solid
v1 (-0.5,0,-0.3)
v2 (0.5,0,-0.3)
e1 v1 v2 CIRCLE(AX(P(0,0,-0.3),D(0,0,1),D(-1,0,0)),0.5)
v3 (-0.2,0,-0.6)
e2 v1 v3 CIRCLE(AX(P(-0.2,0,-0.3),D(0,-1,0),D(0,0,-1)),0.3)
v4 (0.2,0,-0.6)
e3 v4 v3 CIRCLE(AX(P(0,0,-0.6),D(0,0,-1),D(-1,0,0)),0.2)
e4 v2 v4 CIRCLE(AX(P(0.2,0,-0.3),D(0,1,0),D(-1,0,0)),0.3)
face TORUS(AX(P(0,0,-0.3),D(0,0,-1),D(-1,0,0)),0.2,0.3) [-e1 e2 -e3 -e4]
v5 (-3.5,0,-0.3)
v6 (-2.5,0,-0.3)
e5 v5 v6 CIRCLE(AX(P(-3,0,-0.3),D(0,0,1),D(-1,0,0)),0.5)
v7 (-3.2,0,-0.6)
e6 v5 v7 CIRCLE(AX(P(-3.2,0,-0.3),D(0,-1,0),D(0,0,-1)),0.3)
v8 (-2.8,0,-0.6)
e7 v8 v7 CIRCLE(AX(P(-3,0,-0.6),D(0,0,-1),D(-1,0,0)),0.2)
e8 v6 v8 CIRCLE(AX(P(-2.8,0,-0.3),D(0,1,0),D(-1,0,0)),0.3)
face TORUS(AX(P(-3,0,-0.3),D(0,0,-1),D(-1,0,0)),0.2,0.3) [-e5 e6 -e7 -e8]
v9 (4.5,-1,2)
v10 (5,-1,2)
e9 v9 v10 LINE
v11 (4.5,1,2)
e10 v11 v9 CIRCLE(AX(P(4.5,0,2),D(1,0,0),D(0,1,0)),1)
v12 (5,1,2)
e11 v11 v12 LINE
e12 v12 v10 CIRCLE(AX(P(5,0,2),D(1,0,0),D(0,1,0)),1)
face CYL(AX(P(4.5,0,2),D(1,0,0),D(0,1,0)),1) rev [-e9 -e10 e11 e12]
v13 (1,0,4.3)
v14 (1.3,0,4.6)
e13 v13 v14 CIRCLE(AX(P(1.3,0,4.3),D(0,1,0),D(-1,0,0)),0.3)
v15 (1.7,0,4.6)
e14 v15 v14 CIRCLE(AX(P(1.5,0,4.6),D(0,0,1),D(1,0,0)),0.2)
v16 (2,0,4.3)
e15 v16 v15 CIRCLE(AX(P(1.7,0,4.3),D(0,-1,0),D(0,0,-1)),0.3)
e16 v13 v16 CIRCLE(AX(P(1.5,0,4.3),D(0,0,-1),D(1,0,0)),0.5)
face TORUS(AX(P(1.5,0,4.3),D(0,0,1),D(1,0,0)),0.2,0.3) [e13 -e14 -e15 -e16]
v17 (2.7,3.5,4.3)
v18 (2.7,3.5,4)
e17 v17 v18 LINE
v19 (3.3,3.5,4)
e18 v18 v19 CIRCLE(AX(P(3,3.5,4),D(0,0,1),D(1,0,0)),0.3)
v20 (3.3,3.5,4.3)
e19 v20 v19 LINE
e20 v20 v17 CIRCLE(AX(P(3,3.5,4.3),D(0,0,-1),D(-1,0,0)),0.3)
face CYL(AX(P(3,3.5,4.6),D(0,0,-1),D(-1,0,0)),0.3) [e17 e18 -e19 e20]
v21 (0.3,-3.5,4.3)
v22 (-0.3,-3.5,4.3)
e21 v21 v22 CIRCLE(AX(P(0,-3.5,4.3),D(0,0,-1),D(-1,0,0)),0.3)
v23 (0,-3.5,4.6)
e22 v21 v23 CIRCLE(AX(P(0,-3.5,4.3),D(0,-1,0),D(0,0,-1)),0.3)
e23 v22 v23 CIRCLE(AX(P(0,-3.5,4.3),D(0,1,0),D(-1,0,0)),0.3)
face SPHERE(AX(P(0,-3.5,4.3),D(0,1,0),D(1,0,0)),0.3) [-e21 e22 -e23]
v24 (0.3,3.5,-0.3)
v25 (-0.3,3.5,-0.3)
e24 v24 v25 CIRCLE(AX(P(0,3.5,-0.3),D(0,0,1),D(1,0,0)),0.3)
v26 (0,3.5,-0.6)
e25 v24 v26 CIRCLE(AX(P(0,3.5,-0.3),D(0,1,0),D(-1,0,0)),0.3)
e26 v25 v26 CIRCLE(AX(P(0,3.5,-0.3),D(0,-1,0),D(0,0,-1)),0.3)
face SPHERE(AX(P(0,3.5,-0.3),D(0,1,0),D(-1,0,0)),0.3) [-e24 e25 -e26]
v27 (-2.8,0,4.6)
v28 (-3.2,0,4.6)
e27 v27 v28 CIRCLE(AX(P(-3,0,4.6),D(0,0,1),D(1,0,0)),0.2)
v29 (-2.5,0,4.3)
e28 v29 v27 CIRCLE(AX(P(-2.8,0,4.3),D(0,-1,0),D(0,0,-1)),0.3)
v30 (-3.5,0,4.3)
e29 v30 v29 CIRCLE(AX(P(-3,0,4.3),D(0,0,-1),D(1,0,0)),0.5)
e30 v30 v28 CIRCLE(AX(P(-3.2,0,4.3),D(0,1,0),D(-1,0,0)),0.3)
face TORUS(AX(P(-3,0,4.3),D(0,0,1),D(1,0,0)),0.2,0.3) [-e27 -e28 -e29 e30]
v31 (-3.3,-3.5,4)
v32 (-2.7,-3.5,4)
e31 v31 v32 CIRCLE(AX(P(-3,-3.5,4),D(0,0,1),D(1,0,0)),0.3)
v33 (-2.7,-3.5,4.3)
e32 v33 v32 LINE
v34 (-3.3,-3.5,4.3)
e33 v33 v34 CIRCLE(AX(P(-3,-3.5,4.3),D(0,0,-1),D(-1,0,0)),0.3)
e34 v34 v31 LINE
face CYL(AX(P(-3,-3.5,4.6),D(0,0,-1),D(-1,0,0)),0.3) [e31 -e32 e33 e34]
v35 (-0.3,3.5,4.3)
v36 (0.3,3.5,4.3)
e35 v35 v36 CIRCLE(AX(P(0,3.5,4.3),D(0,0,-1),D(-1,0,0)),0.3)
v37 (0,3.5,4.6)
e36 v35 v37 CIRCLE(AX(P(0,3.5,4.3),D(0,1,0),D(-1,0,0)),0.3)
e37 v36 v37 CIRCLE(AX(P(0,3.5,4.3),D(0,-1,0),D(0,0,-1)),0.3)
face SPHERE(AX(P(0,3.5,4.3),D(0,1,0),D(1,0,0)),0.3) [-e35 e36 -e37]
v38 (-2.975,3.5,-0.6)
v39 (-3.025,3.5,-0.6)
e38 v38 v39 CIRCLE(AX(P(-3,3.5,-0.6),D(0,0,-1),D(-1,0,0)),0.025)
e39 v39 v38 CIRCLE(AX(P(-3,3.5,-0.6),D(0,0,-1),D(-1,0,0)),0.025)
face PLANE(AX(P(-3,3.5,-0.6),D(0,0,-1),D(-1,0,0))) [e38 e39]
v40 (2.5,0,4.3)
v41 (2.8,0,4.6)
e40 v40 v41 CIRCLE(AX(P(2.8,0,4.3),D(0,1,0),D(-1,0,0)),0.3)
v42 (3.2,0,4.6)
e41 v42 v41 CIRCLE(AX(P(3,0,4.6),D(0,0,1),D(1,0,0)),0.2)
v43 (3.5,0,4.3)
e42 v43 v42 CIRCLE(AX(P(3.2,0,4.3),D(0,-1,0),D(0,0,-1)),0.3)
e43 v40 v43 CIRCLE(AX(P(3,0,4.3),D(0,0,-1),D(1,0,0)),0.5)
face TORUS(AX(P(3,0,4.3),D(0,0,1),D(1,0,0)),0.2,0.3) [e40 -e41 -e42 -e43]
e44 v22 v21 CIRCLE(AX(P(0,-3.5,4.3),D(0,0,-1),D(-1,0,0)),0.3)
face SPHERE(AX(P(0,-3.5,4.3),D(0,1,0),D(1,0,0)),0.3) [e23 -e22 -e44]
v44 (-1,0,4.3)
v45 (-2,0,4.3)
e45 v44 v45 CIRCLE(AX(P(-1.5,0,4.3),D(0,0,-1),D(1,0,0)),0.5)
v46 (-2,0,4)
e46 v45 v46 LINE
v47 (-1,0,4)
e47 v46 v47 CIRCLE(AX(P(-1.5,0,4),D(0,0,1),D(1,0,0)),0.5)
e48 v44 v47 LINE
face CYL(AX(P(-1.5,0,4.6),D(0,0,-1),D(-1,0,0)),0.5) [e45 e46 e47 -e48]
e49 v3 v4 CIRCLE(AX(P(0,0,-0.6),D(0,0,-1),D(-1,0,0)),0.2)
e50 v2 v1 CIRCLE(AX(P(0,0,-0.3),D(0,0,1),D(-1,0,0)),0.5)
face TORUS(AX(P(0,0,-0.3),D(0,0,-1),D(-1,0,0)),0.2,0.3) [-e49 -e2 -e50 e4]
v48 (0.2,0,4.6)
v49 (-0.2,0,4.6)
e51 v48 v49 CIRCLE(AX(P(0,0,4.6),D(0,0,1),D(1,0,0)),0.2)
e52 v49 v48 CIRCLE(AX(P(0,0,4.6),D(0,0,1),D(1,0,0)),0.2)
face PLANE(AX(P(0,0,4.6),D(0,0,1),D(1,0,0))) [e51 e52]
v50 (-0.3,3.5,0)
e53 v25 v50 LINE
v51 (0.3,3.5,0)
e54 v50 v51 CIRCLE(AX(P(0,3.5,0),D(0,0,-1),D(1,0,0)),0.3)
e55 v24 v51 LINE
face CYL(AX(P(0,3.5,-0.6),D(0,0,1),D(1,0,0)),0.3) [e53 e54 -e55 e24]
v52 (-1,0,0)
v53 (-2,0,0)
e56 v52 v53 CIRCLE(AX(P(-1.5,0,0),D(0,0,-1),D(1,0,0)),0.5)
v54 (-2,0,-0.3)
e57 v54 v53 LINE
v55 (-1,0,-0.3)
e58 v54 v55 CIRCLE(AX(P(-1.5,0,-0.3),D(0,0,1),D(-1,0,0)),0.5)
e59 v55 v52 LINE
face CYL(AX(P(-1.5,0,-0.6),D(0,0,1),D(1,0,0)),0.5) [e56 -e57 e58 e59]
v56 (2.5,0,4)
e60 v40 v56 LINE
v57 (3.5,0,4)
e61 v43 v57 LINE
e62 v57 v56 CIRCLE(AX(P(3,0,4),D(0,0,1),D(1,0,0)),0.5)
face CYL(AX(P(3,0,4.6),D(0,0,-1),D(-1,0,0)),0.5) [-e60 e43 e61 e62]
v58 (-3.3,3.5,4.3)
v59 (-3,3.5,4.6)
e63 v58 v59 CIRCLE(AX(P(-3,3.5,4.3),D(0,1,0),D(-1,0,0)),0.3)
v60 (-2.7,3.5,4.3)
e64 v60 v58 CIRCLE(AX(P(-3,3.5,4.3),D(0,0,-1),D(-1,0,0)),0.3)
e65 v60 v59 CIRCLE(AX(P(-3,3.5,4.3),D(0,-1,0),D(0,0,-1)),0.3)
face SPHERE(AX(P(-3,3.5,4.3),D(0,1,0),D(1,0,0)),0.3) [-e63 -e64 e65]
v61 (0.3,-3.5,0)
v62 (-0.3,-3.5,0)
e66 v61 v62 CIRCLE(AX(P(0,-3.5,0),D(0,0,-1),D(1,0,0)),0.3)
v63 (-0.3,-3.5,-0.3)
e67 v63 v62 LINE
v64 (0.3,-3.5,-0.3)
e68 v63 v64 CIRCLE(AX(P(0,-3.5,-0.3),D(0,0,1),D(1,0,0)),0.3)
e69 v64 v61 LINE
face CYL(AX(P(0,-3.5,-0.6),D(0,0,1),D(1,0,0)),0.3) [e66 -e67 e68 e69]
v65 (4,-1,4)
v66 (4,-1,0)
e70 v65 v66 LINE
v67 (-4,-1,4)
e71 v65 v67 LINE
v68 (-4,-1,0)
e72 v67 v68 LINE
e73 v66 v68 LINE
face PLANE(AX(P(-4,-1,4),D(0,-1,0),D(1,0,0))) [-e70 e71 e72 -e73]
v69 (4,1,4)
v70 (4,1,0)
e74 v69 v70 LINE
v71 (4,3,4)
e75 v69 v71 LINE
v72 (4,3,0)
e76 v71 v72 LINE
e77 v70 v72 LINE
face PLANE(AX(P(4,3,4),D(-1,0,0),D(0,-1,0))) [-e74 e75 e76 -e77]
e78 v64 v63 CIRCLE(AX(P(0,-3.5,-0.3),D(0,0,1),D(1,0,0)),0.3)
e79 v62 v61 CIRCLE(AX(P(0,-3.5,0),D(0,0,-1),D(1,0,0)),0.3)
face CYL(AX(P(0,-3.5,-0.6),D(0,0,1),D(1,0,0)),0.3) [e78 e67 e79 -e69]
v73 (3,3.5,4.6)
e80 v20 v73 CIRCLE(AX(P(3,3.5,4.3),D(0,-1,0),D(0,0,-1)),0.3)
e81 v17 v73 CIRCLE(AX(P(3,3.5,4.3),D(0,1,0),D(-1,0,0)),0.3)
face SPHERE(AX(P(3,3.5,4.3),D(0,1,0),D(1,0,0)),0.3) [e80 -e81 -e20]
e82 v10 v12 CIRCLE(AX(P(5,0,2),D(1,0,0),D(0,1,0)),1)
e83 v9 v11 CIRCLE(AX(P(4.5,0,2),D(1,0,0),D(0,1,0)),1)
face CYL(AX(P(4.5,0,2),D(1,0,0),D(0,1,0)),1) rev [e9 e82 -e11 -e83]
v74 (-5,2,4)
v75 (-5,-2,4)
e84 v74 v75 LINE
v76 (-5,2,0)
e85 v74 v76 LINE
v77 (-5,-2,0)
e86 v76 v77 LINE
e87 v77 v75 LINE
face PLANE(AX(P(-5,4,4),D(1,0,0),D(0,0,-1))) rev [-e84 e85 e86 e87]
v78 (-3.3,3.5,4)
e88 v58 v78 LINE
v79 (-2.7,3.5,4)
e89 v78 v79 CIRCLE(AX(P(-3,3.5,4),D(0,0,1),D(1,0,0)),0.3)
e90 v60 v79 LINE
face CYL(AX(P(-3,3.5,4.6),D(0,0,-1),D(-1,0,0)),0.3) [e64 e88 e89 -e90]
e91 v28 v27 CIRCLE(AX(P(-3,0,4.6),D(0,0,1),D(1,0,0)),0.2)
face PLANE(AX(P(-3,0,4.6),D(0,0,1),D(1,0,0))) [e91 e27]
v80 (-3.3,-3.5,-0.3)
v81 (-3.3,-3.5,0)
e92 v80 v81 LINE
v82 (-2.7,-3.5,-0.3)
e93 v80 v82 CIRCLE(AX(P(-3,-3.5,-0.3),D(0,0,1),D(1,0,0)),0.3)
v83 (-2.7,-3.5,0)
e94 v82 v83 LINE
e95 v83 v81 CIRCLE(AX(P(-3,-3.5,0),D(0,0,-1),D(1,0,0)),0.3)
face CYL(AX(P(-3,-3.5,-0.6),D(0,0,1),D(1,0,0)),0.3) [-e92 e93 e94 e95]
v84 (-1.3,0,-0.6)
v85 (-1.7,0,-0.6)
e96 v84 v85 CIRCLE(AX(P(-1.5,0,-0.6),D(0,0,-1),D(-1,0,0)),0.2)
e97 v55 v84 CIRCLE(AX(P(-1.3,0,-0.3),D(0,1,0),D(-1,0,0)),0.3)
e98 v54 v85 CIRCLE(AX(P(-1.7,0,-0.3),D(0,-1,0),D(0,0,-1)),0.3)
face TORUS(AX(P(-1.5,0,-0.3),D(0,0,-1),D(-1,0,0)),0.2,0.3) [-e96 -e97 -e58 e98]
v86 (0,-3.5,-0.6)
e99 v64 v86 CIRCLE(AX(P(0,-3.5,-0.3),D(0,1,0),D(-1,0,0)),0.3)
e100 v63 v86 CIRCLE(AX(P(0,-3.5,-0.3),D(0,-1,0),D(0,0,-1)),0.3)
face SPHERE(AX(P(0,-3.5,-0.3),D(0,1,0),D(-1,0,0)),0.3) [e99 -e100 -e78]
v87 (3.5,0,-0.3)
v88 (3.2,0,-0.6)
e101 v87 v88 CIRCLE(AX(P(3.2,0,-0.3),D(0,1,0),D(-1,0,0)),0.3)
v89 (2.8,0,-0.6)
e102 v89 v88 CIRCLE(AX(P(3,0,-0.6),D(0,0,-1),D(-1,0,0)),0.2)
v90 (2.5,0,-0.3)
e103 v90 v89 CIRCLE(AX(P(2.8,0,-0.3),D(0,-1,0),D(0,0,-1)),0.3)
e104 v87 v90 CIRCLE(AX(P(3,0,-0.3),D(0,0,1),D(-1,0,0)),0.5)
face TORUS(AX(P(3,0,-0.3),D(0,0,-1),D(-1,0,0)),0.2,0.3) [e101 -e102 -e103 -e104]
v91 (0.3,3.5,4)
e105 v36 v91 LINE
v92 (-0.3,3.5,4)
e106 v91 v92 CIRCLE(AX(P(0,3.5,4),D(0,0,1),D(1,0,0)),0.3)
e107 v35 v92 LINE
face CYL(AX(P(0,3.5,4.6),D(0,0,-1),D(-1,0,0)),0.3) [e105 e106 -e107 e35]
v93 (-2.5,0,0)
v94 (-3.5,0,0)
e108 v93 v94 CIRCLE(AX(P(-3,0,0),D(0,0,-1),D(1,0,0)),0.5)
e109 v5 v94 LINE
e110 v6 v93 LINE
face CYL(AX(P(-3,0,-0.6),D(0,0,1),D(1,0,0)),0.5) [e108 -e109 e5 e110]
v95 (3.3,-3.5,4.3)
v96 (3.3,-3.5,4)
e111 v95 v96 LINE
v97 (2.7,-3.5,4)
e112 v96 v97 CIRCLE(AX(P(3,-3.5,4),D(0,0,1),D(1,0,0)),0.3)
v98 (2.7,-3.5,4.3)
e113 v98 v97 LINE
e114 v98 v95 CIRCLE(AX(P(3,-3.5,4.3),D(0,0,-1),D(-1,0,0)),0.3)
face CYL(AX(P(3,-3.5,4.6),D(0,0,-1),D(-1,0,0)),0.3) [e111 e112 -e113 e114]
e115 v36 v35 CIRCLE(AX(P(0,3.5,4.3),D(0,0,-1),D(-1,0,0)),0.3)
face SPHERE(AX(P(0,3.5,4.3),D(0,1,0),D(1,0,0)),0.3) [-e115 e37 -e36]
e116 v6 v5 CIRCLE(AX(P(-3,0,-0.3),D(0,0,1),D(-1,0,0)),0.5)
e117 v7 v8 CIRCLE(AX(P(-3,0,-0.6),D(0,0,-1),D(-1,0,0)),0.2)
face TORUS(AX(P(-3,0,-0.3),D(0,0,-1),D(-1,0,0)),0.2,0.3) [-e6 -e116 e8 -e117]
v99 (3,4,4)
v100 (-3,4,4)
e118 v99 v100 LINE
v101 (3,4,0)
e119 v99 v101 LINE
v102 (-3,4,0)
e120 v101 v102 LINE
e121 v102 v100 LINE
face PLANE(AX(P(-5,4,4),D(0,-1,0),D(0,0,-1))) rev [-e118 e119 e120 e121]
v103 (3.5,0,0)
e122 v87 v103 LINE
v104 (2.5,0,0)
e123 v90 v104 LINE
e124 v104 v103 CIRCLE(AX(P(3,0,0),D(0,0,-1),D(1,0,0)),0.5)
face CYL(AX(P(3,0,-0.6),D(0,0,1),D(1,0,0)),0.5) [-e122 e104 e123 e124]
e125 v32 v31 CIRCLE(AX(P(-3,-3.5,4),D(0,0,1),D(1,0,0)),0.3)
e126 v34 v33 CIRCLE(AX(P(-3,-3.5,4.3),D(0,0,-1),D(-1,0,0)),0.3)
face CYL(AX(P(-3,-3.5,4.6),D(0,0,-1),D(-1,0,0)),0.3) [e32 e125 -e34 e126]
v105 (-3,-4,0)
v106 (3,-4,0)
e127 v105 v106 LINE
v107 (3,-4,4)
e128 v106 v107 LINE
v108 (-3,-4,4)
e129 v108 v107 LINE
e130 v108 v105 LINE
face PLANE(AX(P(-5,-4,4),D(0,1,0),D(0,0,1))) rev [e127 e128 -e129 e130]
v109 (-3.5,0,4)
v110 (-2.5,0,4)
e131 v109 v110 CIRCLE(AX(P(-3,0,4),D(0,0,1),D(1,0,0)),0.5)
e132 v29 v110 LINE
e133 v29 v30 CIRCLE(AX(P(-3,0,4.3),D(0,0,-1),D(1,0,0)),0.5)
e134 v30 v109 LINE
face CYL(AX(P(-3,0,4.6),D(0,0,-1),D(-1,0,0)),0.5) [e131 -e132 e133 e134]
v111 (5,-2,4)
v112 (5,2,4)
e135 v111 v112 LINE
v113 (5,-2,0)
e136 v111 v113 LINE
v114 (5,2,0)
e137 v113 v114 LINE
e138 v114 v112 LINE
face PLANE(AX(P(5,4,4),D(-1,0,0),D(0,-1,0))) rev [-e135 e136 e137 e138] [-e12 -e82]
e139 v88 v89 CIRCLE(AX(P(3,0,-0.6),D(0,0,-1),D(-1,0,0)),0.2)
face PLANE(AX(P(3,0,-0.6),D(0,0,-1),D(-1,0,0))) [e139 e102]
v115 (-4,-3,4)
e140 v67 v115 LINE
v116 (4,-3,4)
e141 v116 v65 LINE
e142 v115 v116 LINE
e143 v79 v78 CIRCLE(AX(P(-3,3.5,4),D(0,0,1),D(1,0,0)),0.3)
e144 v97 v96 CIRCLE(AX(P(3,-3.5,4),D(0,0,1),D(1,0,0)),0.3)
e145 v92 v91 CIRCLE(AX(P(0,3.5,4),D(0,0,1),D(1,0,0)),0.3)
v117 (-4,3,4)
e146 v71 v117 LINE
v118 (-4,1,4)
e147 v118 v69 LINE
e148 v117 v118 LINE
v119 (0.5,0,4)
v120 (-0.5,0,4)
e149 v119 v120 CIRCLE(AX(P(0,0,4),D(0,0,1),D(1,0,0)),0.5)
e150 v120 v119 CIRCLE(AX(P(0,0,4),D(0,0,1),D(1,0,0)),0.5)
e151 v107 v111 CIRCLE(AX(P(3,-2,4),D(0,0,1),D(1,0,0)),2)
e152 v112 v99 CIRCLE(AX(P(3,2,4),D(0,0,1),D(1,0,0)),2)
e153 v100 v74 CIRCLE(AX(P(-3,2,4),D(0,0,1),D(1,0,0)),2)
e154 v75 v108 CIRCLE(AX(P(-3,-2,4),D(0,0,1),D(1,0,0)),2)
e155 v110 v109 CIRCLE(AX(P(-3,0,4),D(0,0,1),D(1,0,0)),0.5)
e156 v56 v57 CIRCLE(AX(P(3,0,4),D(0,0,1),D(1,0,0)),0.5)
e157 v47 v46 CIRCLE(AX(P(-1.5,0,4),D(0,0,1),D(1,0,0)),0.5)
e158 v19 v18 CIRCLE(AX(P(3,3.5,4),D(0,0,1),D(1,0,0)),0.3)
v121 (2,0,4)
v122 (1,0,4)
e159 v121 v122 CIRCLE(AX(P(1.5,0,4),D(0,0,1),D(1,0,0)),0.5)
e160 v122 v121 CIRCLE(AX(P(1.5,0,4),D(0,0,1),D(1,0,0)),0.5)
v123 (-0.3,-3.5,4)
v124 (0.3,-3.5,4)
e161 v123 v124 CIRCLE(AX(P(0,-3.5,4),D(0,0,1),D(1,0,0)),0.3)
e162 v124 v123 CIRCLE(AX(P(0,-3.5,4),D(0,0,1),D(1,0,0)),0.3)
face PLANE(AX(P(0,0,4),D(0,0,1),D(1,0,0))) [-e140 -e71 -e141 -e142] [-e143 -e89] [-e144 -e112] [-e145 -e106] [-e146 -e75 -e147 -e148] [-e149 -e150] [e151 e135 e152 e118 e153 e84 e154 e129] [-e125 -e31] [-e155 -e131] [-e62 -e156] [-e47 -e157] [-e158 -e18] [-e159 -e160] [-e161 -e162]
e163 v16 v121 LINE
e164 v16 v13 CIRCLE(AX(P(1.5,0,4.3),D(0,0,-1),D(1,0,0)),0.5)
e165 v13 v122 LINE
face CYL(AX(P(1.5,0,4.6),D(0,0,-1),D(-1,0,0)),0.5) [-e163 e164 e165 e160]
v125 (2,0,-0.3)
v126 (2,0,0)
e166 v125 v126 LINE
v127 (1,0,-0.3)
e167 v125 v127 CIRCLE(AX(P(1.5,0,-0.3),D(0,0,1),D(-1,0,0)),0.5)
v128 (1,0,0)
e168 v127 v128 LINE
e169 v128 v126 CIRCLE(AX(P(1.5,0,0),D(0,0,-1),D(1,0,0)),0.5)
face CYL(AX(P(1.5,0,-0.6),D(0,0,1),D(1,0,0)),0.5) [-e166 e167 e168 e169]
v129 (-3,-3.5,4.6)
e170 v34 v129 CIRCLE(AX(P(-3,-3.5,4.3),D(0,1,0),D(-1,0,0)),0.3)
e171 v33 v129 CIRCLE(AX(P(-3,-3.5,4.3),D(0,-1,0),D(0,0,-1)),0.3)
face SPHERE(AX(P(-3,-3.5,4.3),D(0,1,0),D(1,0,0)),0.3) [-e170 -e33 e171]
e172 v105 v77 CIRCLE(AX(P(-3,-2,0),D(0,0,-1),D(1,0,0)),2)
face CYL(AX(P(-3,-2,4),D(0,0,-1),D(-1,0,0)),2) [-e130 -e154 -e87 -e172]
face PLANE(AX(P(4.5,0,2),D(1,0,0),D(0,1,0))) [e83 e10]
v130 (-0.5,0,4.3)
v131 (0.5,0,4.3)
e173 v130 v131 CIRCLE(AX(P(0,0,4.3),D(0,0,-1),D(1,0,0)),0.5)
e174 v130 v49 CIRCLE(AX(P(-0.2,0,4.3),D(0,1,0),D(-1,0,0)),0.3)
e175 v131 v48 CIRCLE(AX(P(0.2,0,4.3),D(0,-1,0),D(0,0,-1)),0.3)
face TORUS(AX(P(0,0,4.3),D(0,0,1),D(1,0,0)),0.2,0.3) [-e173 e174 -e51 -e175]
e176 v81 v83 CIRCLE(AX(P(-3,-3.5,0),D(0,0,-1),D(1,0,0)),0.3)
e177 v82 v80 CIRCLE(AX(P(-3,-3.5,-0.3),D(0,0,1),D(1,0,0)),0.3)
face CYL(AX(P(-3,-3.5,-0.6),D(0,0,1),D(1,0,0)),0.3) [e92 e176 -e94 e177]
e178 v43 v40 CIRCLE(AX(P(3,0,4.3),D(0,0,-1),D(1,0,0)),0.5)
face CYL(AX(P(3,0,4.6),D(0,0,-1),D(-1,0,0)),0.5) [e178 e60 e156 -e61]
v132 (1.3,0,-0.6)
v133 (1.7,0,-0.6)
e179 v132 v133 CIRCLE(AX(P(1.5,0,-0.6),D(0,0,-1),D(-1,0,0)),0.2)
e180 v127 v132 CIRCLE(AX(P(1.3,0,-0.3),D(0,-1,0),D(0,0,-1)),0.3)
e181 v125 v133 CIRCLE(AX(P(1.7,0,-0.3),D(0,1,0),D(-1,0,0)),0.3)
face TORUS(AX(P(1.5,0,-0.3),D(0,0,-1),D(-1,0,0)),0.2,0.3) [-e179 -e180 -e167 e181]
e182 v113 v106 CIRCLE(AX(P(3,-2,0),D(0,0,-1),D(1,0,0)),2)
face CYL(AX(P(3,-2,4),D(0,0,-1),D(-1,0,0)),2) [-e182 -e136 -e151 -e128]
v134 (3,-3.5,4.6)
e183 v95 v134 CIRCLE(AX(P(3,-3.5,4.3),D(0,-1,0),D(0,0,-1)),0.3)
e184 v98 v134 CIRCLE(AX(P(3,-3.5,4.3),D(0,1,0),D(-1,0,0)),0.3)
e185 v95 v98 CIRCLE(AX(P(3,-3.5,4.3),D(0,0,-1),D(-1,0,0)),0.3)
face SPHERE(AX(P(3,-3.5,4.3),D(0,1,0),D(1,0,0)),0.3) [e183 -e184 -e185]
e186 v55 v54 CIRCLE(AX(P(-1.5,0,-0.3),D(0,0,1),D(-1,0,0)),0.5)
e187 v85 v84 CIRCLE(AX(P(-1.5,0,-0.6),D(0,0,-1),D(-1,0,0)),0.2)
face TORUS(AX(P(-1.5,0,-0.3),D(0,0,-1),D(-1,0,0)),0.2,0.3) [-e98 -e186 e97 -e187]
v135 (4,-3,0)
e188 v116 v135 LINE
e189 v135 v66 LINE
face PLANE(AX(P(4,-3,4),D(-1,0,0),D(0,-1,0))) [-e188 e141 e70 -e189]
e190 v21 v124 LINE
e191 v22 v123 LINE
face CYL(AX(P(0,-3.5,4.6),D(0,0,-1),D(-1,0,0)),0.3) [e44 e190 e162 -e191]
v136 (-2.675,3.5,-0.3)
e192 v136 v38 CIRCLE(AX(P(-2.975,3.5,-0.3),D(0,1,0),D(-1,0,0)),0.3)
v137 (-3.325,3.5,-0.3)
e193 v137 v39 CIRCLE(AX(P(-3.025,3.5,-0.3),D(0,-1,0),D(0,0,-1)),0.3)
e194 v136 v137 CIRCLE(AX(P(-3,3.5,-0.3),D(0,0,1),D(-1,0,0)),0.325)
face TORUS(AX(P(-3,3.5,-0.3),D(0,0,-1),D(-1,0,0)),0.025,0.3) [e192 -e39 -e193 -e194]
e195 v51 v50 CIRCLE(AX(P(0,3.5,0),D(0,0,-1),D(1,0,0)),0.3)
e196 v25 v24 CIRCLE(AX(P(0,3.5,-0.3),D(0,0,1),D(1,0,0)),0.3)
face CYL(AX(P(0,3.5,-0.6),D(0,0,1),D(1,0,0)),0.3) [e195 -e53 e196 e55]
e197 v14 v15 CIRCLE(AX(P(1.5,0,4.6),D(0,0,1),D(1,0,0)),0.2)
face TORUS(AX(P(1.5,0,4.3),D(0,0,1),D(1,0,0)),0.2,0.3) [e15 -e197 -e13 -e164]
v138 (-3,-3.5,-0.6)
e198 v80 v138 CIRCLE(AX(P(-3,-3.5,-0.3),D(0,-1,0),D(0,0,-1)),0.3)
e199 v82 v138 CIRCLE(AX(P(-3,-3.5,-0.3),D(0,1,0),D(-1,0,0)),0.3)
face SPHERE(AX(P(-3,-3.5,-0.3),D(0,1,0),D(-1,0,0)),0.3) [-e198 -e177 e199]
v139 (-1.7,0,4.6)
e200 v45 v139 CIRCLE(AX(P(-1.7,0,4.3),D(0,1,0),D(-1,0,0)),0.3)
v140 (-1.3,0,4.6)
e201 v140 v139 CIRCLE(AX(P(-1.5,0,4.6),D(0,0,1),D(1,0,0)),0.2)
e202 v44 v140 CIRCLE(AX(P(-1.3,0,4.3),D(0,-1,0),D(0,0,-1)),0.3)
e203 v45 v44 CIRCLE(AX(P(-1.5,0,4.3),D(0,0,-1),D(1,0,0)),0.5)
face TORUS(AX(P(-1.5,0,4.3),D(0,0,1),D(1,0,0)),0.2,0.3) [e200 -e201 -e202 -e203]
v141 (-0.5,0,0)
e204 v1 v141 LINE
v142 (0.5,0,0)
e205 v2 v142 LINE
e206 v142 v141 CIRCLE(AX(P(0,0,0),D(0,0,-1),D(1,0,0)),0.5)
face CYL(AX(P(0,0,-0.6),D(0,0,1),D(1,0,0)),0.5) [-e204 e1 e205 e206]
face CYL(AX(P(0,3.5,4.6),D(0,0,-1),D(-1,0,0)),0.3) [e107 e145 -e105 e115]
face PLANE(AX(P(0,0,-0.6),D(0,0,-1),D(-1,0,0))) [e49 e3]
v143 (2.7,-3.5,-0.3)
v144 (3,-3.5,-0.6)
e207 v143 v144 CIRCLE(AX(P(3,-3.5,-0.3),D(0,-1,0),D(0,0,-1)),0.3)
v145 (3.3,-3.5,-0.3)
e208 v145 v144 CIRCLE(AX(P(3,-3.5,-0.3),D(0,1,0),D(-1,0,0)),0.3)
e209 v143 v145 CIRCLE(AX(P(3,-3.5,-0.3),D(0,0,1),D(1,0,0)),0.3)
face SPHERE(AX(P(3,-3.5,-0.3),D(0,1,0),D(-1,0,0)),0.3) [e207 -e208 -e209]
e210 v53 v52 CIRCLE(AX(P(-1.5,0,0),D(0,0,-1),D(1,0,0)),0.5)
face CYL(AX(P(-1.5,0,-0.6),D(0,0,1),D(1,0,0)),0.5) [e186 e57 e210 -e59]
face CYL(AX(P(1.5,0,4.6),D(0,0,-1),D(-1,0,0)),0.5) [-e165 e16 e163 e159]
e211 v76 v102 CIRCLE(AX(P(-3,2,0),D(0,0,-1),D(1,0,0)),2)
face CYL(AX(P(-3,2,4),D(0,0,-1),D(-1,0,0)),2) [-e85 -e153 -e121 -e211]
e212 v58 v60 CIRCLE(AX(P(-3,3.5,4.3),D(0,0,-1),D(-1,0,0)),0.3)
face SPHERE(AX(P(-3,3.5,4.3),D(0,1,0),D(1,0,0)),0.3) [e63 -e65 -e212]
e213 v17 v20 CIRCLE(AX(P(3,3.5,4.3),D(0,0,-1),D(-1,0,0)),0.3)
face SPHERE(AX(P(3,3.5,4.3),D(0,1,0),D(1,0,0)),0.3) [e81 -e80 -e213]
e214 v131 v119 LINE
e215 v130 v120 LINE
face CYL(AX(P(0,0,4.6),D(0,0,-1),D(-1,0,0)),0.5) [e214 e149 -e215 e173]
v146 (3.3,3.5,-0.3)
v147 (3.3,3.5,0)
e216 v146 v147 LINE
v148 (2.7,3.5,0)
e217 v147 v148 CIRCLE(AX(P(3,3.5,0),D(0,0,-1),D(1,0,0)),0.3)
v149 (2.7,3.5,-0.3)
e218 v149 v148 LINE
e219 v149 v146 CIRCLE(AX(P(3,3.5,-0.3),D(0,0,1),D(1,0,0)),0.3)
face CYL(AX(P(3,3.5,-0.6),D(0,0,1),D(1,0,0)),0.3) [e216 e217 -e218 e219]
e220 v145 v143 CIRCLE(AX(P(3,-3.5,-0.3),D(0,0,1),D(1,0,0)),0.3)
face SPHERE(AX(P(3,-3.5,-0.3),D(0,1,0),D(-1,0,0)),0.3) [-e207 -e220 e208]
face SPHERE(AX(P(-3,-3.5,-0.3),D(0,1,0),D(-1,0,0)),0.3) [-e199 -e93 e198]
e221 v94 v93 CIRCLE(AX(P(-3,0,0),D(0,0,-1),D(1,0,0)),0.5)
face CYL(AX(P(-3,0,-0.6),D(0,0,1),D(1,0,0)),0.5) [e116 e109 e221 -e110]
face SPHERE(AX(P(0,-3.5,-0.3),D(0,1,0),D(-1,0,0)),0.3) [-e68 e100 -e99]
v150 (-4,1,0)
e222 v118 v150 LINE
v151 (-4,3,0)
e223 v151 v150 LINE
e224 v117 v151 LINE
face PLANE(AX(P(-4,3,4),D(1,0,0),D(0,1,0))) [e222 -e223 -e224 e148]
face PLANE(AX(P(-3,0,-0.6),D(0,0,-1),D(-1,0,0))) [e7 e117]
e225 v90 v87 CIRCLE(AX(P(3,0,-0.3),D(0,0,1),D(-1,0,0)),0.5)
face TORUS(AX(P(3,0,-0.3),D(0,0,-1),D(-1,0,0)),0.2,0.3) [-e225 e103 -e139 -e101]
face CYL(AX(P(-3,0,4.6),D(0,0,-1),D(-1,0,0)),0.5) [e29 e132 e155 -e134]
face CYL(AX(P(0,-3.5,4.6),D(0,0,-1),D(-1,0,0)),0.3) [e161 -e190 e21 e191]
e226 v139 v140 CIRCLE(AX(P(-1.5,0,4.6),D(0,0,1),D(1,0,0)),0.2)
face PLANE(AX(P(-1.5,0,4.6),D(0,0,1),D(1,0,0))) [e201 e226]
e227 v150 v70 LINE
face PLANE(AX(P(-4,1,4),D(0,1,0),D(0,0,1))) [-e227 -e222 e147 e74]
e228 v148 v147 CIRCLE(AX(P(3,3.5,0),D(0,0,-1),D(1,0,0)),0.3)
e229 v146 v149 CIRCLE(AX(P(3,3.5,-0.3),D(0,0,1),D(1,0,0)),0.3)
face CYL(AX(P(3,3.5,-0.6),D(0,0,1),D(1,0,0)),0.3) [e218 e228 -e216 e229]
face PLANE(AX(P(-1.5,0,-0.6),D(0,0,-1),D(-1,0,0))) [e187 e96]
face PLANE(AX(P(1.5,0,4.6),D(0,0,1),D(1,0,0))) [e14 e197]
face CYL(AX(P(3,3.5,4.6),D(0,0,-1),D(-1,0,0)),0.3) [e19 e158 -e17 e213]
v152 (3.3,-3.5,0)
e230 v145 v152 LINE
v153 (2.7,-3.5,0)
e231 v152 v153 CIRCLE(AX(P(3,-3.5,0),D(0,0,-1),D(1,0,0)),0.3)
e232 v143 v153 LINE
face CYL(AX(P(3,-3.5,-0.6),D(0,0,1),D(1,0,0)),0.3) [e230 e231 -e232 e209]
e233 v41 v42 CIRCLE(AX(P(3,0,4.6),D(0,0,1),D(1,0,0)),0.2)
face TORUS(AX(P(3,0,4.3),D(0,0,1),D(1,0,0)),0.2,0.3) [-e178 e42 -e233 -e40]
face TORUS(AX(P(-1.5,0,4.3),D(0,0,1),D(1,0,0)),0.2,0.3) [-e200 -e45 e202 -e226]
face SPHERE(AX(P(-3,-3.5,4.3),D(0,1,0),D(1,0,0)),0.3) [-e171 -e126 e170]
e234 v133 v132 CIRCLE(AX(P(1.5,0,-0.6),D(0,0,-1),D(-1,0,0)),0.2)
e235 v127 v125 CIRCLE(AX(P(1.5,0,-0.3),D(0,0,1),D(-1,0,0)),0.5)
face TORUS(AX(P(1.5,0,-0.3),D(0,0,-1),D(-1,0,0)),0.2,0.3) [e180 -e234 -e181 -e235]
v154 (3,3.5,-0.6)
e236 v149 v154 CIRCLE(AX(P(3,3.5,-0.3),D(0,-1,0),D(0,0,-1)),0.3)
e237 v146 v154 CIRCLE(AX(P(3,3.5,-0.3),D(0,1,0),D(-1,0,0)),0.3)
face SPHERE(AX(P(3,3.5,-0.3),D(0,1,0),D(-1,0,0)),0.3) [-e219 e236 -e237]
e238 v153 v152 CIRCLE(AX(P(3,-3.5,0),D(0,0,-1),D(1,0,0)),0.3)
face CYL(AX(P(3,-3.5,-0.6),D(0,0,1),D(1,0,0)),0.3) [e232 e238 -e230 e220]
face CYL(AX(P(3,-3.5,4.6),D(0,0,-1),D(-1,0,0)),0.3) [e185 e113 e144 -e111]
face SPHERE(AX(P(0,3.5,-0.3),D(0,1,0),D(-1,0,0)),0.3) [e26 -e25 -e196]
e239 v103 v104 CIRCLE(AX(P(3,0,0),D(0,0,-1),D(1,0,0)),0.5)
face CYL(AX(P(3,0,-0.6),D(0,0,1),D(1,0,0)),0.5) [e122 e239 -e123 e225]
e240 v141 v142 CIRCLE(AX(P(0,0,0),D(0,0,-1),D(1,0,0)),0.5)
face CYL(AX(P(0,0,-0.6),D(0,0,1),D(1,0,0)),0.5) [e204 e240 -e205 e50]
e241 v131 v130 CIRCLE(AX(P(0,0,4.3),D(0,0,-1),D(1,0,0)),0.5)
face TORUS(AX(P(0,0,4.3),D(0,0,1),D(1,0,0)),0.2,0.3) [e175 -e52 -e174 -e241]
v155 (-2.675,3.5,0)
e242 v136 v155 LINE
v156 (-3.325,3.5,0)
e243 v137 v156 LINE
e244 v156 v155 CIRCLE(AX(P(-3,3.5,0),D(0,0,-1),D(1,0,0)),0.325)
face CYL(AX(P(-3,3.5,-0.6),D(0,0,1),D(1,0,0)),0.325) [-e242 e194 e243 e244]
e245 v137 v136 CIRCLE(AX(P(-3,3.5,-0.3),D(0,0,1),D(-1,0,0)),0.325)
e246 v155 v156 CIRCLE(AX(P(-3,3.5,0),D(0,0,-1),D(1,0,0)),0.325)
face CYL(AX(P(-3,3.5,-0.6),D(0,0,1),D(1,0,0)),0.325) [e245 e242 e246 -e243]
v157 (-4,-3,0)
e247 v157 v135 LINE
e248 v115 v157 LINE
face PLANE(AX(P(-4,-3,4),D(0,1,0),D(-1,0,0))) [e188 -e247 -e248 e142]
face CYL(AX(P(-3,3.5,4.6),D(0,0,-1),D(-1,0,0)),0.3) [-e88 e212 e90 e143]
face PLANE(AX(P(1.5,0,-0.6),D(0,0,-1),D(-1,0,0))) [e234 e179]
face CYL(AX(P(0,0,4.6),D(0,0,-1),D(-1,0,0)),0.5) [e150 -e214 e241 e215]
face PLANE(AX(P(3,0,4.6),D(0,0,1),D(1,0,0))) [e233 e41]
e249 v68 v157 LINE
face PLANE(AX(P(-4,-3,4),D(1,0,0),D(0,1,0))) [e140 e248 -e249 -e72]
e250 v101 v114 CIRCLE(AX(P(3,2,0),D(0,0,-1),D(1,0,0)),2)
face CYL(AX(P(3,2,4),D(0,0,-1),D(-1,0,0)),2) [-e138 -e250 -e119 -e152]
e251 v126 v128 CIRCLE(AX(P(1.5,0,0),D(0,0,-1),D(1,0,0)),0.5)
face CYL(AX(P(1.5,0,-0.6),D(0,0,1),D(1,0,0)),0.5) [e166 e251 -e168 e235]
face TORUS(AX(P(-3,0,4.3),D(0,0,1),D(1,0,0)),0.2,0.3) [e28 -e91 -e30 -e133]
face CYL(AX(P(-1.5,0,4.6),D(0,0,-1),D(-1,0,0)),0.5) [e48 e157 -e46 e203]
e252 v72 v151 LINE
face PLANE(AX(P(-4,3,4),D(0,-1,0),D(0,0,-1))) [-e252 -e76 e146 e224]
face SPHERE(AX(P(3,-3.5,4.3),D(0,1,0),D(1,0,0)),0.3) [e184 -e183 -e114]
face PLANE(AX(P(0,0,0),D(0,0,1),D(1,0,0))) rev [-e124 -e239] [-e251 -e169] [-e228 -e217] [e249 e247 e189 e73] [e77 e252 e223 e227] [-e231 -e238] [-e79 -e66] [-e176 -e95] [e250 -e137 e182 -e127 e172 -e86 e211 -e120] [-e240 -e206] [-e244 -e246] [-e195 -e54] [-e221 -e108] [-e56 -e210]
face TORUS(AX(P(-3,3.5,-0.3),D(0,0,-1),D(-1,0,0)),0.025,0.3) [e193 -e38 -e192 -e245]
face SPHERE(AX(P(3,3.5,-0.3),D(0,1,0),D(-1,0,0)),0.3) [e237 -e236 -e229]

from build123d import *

# Parameters (mm, degrees)
SKETCH1_W           = 10
SKETCH1_H           = 8
SKETCH1_W_2         = 8
SKETCH1_H_2         = 2
BOSS_EXTRUDE3_DEPTH = 4
SKETCH2_R           = 1
CUT_EXTRUDE6_DEPTH  = 0.5
FILLET1_R           = 2
SKETCH4_R           = 0.5
SKETCH4_R_2         = 0.3
BOSS_EXTRUDE7_DEPTH = 0.6
FILLET4_R           = 0.3
BOSS_EXTRUDE8_START = 0.6
SKETCH5_R           = 0.5
SKETCH5_R_2         = 0.3
SKETCH5_R_3         = 0.325
BOSS_EXTRUDE8_DEPTH = 0.6
FILLET5_R           = 0.3
FILLET6_R           = 0.3
FILLET7_R           = 0.3


with BuildPart() as part:
    # Sketch1 → Boss-Extrude3 (new body)
    with BuildSketch(Plane.XY):
        Rectangle(SKETCH1_W, SKETCH1_H)
        with Locations((0, 2)):
            Rectangle(SKETCH1_W_2, SKETCH1_H_2, mode=Mode.SUBTRACT)
        with Locations((0, -2)):
            Rectangle(SKETCH1_W_2, SKETCH1_H_2, mode=Mode.SUBTRACT)
    extrude(amount=BOSS_EXTRUDE3_DEPTH)

    # Sketch2 → Cut-Extrude6 (cut)
    with BuildSketch(Plane(origin=(5, 0, 0), x_dir=(0, 0, -1), z_dir=(1, 0, 0))):
        with Locations(Location((-2, 0, 0), (0, 0, 90))):
            Circle(SKETCH2_R)
    extrude(amount=-CUT_EXTRUDE6_DEPTH, mode=Mode.SUBTRACT)

    # Fillet1
    fillet1_edges = [part.edges().sort_by_distance(p)[0] for p in [
        (5, -4, 2),
        (-5, -4, 2),
        (-5, 4, 2),
        (5, 4, 2),
    ]]
    fillet(fillet1_edges, radius=FILLET1_R)

    # Sketch4 → Boss-Extrude7 (add)
    with BuildSketch(Plane.XY.offset(4)):
        Circle(SKETCH4_R)
        with Locations((-1.5, 0)):
            Circle(SKETCH4_R)
        with Locations((-3, 0)):
            Circle(SKETCH4_R)
        with Locations((1.5, 0)):
            Circle(SKETCH4_R)
        with Locations((3, 0)):
            Circle(SKETCH4_R)
        with Locations((3, -3.5)):
            Circle(SKETCH4_R_2)
        with Locations((0, -3.5)):
            Circle(SKETCH4_R_2)
        with Locations((-3, -3.5)):
            Circle(SKETCH4_R_2)
        with Locations((3, 3.5)):
            Circle(SKETCH4_R_2)
        with Locations((0, 3.5)):
            Circle(SKETCH4_R_2)
        with Locations((-3, 3.5)):
            Circle(SKETCH4_R_2)
    extrude(amount=BOSS_EXTRUDE7_DEPTH)

    # Fillet4
    fillet4_edges = [part.edges().sort_by_distance(p)[0] for p in [
        (-0.5, 0, 4.6),
        (-2, 0, 4.6),
        (-3.5, 0, 4.6),
        (1, 0, 4.6),
        (2.5, 0, 4.6),
    ]]
    fillet(fillet4_edges, radius=FILLET4_R)

    # Sketch5 → Boss-Extrude8 (add)
    with BuildSketch(Plane(origin=(0, 0, 0), x_dir=(-1, 0, 0), z_dir=(0, 0, -1)).offset(BOSS_EXTRUDE8_START)):
        with Locations(Location((0, 0, 0), (0, 0, 180))):
            Circle(SKETCH5_R)
        with Locations(Location((1.5, 0, 0), (0, 0, 180))):
            Circle(SKETCH5_R)
        with Locations(Location((3, 0, 0), (0, 0, 180))):
            Circle(SKETCH5_R)
        with Locations(Location((-1.5, 0, 0), (0, 0, 180))):
            Circle(SKETCH5_R)
        with Locations(Location((-3, 0, 0), (0, 0, 180))):
            Circle(SKETCH5_R)
        with Locations(Location((-3, 3.5, 0), (0, 0, 180))):
            Circle(SKETCH5_R_2)
        with Locations(Location((0, 3.5, 0), (0, 0, 180))):
            Circle(SKETCH5_R_2)
        with Locations(Location((3, 3.5, 0), (0, 0, 180))):
            Circle(SKETCH5_R_3)
        with Locations(Location((-3, -3.5, 0), (0, 0, 180))):
            Circle(SKETCH5_R_2)
        with Locations(Location((0, -3.5, 0), (0, 0, 180))):
            Circle(SKETCH5_R_2)
        with Locations(Location((3, -3.5, 0), (0, 0, 180))):
            Circle(SKETCH5_R_2)
    extrude(amount=-BOSS_EXTRUDE8_DEPTH)

    # Fillet5
    fillet5_edges = [part.edges().sort_by_distance(p)[0] for p in [
        (-0.5, 0, -0.6),
        (-2, 0, -0.6),
        (-3.5, 0, -0.6),
        (1, 0, -0.6),
        (2.5, 0, -0.6),
    ]]
    fillet(fillet5_edges, radius=FILLET5_R)

    # Fillet6
    fillet6_edges = [part.edges().sort_by_distance(p)[0] for p in [
        (-0.3, 3.5, 4.6),
        (-3.3, 3.5, 4.6),
        (2.7, -3.5, 4.6),
        (-0.3, -3.5, 4.6),
        (-3.3, -3.5, 4.6),
        (2.7, 3.5, 4.6),
    ]]
    fillet(fillet6_edges, radius=FILLET6_R)

    # Fillet7
    fillet7_edges = [part.edges().sort_by_distance(p)[0] for p in [
        (2.7, 3.5, -0.6),
        (-0.3, 3.5, -0.6),
        (-3.325, 3.5, -0.6),
        (2.7, -3.5, -0.6),
        (-0.3, -3.5, -0.6),
        (-3.3, -3.5, -0.6),
    ]]
    fillet(fillet7_edges, radius=FILLET7_R)


solid = part.part
